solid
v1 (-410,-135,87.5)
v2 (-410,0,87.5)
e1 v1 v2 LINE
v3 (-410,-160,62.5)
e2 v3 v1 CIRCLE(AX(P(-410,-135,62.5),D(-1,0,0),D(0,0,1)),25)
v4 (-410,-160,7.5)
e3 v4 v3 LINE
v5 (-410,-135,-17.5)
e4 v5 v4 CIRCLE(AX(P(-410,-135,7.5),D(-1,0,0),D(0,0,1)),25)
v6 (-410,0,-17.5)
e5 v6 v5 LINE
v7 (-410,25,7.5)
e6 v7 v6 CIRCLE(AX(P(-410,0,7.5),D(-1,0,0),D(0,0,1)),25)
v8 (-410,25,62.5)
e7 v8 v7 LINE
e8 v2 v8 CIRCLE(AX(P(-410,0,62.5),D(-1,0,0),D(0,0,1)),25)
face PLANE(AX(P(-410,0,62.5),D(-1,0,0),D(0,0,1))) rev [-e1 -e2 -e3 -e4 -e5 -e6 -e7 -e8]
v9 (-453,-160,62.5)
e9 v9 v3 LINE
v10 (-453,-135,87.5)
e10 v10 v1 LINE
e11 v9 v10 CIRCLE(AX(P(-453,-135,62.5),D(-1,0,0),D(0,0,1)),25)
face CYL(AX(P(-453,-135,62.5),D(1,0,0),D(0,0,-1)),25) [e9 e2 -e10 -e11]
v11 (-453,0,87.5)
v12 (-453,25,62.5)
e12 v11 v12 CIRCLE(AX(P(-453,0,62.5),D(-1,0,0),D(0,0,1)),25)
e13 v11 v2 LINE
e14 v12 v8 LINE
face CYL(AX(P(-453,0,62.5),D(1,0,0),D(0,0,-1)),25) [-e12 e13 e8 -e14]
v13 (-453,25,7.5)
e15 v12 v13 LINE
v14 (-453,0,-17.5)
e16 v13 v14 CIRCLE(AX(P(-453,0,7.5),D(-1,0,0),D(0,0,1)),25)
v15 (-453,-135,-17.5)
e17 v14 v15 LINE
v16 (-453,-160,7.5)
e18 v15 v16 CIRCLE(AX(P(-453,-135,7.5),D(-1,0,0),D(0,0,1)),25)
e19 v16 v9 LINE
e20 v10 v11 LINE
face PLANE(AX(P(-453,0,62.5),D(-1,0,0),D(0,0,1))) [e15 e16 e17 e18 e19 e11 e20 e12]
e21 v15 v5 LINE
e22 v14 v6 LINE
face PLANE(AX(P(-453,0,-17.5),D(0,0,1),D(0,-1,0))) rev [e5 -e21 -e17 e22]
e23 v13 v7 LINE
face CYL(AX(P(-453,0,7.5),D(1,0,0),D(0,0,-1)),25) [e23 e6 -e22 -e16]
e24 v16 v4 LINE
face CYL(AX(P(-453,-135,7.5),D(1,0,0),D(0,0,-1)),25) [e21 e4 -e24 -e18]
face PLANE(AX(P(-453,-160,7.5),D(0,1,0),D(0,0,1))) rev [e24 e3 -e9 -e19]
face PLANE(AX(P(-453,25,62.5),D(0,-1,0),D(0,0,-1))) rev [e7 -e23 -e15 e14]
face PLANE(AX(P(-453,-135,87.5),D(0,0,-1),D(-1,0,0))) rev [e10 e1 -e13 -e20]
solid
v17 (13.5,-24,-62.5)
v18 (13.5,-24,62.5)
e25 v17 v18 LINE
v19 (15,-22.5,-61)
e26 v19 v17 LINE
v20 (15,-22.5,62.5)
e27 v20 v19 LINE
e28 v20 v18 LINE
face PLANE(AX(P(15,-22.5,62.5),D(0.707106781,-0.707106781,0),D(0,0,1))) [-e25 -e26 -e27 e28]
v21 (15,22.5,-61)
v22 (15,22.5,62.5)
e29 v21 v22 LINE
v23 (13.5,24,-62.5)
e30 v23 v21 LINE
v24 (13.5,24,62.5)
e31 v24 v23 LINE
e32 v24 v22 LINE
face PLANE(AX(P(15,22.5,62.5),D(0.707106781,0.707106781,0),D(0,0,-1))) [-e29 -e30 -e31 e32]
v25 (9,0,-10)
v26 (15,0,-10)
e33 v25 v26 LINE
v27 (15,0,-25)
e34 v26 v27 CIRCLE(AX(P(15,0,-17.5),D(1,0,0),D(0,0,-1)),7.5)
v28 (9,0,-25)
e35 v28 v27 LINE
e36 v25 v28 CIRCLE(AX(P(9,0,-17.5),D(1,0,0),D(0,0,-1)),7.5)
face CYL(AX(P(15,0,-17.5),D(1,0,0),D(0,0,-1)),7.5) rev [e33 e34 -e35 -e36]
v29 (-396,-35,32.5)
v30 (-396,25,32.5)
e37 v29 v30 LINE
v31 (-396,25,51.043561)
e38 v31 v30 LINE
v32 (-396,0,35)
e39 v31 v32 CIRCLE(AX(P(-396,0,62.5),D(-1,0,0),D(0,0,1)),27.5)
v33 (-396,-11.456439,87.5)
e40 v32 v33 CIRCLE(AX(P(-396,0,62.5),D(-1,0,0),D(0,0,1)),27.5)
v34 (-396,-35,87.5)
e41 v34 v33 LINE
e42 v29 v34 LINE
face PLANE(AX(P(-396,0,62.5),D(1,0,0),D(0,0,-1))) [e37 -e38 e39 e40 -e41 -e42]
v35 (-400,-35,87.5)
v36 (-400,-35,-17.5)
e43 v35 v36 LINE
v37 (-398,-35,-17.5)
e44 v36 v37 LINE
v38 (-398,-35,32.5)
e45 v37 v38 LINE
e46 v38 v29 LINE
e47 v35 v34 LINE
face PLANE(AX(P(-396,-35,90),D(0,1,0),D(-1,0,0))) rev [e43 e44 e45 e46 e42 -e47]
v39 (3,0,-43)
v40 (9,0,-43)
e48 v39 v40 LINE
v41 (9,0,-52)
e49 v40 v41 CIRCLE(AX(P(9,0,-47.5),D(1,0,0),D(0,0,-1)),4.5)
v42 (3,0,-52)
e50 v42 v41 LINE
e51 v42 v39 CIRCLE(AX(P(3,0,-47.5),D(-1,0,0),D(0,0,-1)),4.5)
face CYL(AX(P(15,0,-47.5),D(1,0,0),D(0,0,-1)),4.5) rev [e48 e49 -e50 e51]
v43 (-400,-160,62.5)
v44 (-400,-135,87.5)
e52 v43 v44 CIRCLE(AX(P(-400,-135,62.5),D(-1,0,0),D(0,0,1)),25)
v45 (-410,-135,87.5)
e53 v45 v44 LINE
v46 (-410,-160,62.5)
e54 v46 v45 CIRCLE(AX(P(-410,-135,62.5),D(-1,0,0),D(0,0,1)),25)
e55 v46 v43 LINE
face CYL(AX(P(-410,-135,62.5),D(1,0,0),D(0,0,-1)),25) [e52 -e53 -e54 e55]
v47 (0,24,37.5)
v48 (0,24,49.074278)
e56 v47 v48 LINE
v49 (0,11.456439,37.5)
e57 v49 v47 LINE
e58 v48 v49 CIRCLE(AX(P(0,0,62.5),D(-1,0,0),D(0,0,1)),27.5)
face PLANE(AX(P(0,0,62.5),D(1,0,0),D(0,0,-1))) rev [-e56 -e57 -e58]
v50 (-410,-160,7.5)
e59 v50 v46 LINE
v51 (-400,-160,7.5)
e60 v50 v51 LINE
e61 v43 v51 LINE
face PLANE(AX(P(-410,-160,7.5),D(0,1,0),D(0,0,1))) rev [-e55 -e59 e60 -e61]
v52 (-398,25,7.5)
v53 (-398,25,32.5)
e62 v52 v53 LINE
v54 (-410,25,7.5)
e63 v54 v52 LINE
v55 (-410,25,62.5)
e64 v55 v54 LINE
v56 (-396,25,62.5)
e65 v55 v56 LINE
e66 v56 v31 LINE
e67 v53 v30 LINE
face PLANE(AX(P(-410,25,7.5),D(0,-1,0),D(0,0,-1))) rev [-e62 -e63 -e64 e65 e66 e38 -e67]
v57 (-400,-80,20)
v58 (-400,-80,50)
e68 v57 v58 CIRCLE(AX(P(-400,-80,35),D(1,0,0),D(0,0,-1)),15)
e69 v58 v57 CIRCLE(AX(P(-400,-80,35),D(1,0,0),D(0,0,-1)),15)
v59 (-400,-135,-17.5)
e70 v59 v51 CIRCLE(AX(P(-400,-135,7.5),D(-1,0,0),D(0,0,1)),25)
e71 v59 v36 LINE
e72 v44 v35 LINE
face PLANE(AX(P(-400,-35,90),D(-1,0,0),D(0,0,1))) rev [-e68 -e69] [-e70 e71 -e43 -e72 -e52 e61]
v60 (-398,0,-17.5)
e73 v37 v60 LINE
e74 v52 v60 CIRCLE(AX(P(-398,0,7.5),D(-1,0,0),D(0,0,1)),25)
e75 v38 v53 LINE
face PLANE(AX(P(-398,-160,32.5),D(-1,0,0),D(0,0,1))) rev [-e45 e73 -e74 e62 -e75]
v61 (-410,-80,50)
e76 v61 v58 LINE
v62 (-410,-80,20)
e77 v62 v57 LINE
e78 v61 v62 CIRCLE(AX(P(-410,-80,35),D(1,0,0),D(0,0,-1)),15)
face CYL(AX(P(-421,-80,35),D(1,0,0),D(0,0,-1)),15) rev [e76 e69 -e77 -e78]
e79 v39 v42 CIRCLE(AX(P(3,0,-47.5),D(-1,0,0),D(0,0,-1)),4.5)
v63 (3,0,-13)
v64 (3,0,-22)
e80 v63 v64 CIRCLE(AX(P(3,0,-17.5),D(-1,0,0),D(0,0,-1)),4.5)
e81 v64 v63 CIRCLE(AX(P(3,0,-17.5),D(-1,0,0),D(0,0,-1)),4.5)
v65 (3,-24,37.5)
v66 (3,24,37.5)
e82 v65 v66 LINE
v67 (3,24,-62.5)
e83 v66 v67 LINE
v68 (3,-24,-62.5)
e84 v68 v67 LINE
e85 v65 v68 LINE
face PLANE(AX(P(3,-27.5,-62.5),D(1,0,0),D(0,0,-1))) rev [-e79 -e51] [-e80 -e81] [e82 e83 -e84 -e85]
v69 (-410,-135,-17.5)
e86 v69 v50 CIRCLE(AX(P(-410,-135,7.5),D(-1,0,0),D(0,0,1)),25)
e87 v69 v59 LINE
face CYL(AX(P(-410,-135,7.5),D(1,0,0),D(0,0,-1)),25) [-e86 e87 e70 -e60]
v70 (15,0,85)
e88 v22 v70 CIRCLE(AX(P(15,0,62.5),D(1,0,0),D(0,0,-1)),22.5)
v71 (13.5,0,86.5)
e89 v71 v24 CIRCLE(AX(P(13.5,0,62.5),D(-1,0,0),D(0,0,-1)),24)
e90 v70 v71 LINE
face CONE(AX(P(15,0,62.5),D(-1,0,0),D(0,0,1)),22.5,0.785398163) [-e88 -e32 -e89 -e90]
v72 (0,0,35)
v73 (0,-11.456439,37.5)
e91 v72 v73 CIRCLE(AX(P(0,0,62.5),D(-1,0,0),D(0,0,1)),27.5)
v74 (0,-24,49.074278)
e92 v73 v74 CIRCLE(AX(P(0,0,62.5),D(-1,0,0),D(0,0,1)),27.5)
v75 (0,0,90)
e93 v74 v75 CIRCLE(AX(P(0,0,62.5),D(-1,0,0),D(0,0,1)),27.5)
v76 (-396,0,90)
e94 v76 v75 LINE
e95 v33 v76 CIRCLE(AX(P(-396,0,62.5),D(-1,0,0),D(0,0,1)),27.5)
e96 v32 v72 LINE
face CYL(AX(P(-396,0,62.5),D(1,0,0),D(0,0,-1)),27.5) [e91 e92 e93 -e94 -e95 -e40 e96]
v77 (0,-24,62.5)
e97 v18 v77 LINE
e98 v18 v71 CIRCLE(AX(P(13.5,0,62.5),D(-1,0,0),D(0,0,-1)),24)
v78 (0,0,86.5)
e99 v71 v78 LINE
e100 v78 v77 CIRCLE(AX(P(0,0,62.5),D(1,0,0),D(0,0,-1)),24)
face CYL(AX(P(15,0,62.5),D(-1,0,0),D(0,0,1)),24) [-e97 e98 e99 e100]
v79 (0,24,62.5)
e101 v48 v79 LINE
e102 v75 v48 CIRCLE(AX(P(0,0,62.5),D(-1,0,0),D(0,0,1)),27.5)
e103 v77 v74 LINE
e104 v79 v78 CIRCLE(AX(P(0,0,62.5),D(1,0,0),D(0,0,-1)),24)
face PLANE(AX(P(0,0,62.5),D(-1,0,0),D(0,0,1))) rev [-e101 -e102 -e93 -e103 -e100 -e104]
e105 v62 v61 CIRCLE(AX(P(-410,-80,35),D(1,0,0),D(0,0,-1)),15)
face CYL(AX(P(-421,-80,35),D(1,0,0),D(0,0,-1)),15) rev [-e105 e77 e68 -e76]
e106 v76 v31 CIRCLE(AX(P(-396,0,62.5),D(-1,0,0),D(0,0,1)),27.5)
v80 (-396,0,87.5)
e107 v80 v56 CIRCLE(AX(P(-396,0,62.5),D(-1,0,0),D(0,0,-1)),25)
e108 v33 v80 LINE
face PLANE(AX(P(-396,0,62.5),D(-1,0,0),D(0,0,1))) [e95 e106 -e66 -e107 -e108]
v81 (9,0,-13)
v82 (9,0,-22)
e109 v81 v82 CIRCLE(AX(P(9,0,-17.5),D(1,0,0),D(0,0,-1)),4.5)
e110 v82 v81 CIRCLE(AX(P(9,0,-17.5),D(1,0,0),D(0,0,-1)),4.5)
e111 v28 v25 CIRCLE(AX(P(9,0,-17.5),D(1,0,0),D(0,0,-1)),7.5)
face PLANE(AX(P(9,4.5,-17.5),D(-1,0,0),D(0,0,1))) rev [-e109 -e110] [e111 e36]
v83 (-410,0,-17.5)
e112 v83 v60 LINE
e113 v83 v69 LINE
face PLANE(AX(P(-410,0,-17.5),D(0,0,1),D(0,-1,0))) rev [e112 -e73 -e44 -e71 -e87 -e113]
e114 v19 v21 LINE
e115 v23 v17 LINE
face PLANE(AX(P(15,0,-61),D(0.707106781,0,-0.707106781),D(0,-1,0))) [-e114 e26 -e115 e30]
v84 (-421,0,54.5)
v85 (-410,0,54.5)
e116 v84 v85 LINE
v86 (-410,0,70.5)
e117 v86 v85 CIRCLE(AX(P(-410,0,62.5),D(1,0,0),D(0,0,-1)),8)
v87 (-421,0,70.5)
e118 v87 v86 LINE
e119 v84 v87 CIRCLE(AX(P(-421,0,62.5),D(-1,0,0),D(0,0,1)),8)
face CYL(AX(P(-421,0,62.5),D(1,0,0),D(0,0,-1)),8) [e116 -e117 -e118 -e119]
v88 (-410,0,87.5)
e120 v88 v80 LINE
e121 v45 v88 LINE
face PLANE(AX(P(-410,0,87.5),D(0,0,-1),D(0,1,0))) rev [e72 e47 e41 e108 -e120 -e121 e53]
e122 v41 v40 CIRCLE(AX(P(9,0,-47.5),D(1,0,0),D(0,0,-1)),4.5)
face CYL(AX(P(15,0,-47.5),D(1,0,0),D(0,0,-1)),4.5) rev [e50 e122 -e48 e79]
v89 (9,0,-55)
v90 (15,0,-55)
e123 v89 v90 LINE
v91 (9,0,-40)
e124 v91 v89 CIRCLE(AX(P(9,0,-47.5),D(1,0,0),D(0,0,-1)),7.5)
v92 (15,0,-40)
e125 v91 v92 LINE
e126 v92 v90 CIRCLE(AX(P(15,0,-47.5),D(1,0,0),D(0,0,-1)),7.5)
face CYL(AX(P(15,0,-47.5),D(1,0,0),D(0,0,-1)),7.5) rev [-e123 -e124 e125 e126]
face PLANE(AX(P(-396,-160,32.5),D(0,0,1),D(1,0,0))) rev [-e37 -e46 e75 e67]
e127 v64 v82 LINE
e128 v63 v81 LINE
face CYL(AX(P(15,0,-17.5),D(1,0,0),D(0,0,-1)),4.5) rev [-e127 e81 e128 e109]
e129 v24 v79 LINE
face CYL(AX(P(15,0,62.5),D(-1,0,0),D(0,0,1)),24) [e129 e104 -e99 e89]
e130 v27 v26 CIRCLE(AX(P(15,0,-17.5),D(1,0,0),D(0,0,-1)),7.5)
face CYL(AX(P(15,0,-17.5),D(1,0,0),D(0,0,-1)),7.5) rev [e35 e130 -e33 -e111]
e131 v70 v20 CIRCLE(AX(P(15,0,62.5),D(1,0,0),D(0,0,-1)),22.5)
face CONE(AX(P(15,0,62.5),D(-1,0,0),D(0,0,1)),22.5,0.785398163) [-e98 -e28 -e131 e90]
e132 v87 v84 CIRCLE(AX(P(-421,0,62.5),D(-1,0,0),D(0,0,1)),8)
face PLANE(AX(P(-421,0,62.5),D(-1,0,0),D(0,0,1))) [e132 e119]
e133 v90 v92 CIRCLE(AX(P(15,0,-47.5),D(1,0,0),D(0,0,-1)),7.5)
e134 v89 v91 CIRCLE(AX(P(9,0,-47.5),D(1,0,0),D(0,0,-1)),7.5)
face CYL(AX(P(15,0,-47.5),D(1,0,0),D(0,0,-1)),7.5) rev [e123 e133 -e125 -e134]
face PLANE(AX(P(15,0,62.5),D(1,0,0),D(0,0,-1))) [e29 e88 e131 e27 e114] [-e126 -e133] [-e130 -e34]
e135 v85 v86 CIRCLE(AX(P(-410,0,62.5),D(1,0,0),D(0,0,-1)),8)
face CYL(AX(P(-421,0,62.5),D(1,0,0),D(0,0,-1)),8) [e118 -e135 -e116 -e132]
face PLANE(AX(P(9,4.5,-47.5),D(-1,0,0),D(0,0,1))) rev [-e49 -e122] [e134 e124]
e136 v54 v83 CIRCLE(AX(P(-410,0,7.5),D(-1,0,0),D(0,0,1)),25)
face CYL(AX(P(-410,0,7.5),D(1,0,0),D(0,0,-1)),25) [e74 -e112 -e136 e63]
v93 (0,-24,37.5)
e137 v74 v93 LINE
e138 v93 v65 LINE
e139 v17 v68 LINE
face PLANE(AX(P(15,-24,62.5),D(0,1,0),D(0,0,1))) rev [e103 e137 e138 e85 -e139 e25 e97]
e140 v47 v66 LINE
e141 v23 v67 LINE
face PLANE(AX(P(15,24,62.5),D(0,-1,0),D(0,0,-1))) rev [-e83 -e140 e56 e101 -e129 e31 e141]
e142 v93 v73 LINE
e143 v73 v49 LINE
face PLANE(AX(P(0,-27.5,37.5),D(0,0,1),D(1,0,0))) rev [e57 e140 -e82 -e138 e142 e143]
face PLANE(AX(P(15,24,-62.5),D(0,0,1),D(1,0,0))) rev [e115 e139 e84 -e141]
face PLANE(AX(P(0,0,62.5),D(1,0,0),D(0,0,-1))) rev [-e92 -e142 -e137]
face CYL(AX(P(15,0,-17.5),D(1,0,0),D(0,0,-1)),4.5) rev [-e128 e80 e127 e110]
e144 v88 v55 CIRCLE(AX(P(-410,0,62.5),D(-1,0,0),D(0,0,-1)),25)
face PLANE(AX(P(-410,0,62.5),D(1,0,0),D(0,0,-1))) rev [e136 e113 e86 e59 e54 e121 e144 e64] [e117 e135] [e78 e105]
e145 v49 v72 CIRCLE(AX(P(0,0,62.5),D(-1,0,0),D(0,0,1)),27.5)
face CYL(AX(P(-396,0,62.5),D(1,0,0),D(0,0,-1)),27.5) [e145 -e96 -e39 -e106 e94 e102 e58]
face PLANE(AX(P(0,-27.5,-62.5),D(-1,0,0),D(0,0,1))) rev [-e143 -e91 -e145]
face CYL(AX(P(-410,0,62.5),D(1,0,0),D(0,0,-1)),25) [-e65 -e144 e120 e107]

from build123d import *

# Parameters (mm, degrees)
EXTRUDE_1_DEPTH           = 15
SKETCH_2_R                = 27.5
EXTRUDE_2_DEPTH           = 396
HOLE_WIZARD_1_D           = 9
HOLE_WIZARD_1_CBORE_D     = 15
HOLE_WIZARD_1_CBORE_DEPTH = 6
CHAMFER_1_SIZE            = 1.5
SKETCH_5_W                = 3
SKETCH_5_H                = 100
CUT_EXTRUDE_1_DEPTH       = 410.351010748
SKETCH_6_R                = 8
EXTRUDE_3_DEPTH           = 25
EXTRUDE_4_DEPTH           = 14
SKETCH_8_W                = 4
SKETCH_8_H                = 125
CUT_EXTRUDE_2_DEPTH       = 464.030506554
SKETCH_9_R                = 15
CUT_EXTRUDE_3_DEPTH       = 454.789598823
SKETCH_10_W               = 2
SKETCH_10_H               = 50
CUT_EXTRUDE_4_DEPTH       = 469.578702034
EXTRUDE_5_DEPTH           = 43


with BuildPart() as part:
    # 草图1 → 凸台-拉伸1 (new body)
    with BuildSketch(Plane(origin=(0, 0, 0), x_dir=(0, 0, -1), z_dir=(1, 0, 0))):
        with BuildLine():
            Line((-62.5, 24), (62.5, 24))
            Line((62.5, 24), (62.5, -24))
            Line((62.5, -24), (-62.5, -24))
            ThreePointArc((-62.5, -24), (-86.5, 0), (-62.5, 24))
        make_face()
    extrude(amount=EXTRUDE_1_DEPTH)

    # 草图2 → 凸台-拉伸2 (add)
    with BuildSketch(Plane.ZY):
        with Locations(Location((62.5, 0, 0), (0, 0, 240.777129706))):
            Circle(SKETCH_2_R)
    extrude(amount=EXTRUDE_2_DEPTH)

    # 打孔尺寸(%根据)内六角花形圆柱头螺钉1 (through all)
    with Locations(Plane(origin=(15, 0, 0), x_dir=(0, 0, -1), z_dir=(1, 0, 0))):
        with Locations((17.5, 0), (47.5, 0)):
            CounterBoreHole(HOLE_WIZARD_1_D / 2, HOLE_WIZARD_1_CBORE_D / 2, HOLE_WIZARD_1_CBORE_DEPTH)

    # 倒角1
    chamfer_1_edges = [part.edges().sort_by_distance(p)[0] for p in [
        (15, 0, 86.5),
        (15, -24, 0),
        (15, 0, -62.5),
        (15, 24, 0),
    ]]
    chamfer(chamfer_1_edges, length=CHAMFER_1_SIZE)

    # 草图5 → 切除-拉伸1 (cut, through all)
    with BuildSketch(Plane(origin=(0, 24, 0), x_dir=(1, 0, 0), z_dir=(0, 1, 0))):
        with Locations((1.5, 12.5)):
            Rectangle(SKETCH_5_W, SKETCH_5_H)
    extrude(amount=-CUT_EXTRUDE_1_DEPTH, mode=Mode.SUBTRACT)

    # 草图6 → 凸台-拉伸3 (add)
    with BuildSketch(Plane.ZY.offset(396)):
        with Locations((62.5, 0)):
            Circle(SKETCH_6_R)
    extrude(amount=EXTRUDE_3_DEPTH)

    # 草图7 → 凸台-拉伸4 (add)
    with BuildSketch(Plane.ZY.offset(396)):
        with BuildLine():
            Line((7.5, 25), (62.5, 25))
            ThreePointArc((62.5, 25), (80.17766953, 17.67766953), (87.5, 0))
            Line((87.5, 0), (87.5, -135))
            ThreePointArc((87.5, -135), (80.17766953, -152.67766953), (62.5, -160))
            Line((62.5, -160), (7.5, -160))
            ThreePointArc((7.5, -160), (-10.17766953, -152.67766953), (-17.5, -135))
            Line((-17.5, -135), (-17.5, 0))
            ThreePointArc((-17.5, 0), (-10.17766953, 17.67766953), (7.5, 25))
        make_face()
    extrude(amount=EXTRUDE_4_DEPTH)

    # 草图8 → 切除-拉伸2 (cut, through all)
    with BuildSketch(Plane(origin=(0, 0, -17.5), x_dir=(-1, 0, 0), z_dir=(0, 0, -1))):
        with Locations((398, -97.5)):
            Rectangle(SKETCH_8_W, SKETCH_8_H)
    extrude(amount=-CUT_EXTRUDE_2_DEPTH, mode=Mode.SUBTRACT)

    # 草图9 → 切除-拉伸3 (cut, through all)
    with BuildSketch(Plane(origin=(-400, 0, 0), x_dir=(0, 0, -1), z_dir=(1, 0, 0))):
        with Locations((-35, -80)):
            Circle(SKETCH_9_R)
    extrude(amount=-CUT_EXTRUDE_3_DEPTH, mode=Mode.SUBTRACT)

    # 草图10 → 切除-拉伸4 (cut, through all)
    with BuildSketch(Plane(origin=(0, 25, 0), x_dir=(1, 0, 0), z_dir=(0, 1, 0))):
        with Locations((-397, -7.5)):
            Rectangle(SKETCH_10_W, SKETCH_10_H)
    extrude(amount=-CUT_EXTRUDE_4_DEPTH, mode=Mode.SUBTRACT)


with BuildPart() as body_2:
    # 草图11 → 凸台-拉伸5 (new body)
    with BuildSketch(Plane.ZY.offset(410)):
        with BuildLine():
            Line((62.5, 25), (7.5, 25))
            ThreePointArc((7.5, 25), (-10.17766953, 17.67766953), (-17.5, 0))
            Line((-17.5, 0), (-17.5, -135))
            ThreePointArc((-17.5, -135), (-10.17766953, -152.67766953), (7.5, -160))
            Line((7.5, -160), (62.5, -160))
            ThreePointArc((62.5, -160), (80.17766953, -152.67766953), (87.5, -135))
            Line((87.5, -135), (87.5, 0))
            ThreePointArc((87.5, 0), (80.17766953, 17.67766953), (62.5, 25))
        make_face()
    extrude(amount=EXTRUDE_5_DEPTH)


solid = Compound([part.part, body_2.part])
